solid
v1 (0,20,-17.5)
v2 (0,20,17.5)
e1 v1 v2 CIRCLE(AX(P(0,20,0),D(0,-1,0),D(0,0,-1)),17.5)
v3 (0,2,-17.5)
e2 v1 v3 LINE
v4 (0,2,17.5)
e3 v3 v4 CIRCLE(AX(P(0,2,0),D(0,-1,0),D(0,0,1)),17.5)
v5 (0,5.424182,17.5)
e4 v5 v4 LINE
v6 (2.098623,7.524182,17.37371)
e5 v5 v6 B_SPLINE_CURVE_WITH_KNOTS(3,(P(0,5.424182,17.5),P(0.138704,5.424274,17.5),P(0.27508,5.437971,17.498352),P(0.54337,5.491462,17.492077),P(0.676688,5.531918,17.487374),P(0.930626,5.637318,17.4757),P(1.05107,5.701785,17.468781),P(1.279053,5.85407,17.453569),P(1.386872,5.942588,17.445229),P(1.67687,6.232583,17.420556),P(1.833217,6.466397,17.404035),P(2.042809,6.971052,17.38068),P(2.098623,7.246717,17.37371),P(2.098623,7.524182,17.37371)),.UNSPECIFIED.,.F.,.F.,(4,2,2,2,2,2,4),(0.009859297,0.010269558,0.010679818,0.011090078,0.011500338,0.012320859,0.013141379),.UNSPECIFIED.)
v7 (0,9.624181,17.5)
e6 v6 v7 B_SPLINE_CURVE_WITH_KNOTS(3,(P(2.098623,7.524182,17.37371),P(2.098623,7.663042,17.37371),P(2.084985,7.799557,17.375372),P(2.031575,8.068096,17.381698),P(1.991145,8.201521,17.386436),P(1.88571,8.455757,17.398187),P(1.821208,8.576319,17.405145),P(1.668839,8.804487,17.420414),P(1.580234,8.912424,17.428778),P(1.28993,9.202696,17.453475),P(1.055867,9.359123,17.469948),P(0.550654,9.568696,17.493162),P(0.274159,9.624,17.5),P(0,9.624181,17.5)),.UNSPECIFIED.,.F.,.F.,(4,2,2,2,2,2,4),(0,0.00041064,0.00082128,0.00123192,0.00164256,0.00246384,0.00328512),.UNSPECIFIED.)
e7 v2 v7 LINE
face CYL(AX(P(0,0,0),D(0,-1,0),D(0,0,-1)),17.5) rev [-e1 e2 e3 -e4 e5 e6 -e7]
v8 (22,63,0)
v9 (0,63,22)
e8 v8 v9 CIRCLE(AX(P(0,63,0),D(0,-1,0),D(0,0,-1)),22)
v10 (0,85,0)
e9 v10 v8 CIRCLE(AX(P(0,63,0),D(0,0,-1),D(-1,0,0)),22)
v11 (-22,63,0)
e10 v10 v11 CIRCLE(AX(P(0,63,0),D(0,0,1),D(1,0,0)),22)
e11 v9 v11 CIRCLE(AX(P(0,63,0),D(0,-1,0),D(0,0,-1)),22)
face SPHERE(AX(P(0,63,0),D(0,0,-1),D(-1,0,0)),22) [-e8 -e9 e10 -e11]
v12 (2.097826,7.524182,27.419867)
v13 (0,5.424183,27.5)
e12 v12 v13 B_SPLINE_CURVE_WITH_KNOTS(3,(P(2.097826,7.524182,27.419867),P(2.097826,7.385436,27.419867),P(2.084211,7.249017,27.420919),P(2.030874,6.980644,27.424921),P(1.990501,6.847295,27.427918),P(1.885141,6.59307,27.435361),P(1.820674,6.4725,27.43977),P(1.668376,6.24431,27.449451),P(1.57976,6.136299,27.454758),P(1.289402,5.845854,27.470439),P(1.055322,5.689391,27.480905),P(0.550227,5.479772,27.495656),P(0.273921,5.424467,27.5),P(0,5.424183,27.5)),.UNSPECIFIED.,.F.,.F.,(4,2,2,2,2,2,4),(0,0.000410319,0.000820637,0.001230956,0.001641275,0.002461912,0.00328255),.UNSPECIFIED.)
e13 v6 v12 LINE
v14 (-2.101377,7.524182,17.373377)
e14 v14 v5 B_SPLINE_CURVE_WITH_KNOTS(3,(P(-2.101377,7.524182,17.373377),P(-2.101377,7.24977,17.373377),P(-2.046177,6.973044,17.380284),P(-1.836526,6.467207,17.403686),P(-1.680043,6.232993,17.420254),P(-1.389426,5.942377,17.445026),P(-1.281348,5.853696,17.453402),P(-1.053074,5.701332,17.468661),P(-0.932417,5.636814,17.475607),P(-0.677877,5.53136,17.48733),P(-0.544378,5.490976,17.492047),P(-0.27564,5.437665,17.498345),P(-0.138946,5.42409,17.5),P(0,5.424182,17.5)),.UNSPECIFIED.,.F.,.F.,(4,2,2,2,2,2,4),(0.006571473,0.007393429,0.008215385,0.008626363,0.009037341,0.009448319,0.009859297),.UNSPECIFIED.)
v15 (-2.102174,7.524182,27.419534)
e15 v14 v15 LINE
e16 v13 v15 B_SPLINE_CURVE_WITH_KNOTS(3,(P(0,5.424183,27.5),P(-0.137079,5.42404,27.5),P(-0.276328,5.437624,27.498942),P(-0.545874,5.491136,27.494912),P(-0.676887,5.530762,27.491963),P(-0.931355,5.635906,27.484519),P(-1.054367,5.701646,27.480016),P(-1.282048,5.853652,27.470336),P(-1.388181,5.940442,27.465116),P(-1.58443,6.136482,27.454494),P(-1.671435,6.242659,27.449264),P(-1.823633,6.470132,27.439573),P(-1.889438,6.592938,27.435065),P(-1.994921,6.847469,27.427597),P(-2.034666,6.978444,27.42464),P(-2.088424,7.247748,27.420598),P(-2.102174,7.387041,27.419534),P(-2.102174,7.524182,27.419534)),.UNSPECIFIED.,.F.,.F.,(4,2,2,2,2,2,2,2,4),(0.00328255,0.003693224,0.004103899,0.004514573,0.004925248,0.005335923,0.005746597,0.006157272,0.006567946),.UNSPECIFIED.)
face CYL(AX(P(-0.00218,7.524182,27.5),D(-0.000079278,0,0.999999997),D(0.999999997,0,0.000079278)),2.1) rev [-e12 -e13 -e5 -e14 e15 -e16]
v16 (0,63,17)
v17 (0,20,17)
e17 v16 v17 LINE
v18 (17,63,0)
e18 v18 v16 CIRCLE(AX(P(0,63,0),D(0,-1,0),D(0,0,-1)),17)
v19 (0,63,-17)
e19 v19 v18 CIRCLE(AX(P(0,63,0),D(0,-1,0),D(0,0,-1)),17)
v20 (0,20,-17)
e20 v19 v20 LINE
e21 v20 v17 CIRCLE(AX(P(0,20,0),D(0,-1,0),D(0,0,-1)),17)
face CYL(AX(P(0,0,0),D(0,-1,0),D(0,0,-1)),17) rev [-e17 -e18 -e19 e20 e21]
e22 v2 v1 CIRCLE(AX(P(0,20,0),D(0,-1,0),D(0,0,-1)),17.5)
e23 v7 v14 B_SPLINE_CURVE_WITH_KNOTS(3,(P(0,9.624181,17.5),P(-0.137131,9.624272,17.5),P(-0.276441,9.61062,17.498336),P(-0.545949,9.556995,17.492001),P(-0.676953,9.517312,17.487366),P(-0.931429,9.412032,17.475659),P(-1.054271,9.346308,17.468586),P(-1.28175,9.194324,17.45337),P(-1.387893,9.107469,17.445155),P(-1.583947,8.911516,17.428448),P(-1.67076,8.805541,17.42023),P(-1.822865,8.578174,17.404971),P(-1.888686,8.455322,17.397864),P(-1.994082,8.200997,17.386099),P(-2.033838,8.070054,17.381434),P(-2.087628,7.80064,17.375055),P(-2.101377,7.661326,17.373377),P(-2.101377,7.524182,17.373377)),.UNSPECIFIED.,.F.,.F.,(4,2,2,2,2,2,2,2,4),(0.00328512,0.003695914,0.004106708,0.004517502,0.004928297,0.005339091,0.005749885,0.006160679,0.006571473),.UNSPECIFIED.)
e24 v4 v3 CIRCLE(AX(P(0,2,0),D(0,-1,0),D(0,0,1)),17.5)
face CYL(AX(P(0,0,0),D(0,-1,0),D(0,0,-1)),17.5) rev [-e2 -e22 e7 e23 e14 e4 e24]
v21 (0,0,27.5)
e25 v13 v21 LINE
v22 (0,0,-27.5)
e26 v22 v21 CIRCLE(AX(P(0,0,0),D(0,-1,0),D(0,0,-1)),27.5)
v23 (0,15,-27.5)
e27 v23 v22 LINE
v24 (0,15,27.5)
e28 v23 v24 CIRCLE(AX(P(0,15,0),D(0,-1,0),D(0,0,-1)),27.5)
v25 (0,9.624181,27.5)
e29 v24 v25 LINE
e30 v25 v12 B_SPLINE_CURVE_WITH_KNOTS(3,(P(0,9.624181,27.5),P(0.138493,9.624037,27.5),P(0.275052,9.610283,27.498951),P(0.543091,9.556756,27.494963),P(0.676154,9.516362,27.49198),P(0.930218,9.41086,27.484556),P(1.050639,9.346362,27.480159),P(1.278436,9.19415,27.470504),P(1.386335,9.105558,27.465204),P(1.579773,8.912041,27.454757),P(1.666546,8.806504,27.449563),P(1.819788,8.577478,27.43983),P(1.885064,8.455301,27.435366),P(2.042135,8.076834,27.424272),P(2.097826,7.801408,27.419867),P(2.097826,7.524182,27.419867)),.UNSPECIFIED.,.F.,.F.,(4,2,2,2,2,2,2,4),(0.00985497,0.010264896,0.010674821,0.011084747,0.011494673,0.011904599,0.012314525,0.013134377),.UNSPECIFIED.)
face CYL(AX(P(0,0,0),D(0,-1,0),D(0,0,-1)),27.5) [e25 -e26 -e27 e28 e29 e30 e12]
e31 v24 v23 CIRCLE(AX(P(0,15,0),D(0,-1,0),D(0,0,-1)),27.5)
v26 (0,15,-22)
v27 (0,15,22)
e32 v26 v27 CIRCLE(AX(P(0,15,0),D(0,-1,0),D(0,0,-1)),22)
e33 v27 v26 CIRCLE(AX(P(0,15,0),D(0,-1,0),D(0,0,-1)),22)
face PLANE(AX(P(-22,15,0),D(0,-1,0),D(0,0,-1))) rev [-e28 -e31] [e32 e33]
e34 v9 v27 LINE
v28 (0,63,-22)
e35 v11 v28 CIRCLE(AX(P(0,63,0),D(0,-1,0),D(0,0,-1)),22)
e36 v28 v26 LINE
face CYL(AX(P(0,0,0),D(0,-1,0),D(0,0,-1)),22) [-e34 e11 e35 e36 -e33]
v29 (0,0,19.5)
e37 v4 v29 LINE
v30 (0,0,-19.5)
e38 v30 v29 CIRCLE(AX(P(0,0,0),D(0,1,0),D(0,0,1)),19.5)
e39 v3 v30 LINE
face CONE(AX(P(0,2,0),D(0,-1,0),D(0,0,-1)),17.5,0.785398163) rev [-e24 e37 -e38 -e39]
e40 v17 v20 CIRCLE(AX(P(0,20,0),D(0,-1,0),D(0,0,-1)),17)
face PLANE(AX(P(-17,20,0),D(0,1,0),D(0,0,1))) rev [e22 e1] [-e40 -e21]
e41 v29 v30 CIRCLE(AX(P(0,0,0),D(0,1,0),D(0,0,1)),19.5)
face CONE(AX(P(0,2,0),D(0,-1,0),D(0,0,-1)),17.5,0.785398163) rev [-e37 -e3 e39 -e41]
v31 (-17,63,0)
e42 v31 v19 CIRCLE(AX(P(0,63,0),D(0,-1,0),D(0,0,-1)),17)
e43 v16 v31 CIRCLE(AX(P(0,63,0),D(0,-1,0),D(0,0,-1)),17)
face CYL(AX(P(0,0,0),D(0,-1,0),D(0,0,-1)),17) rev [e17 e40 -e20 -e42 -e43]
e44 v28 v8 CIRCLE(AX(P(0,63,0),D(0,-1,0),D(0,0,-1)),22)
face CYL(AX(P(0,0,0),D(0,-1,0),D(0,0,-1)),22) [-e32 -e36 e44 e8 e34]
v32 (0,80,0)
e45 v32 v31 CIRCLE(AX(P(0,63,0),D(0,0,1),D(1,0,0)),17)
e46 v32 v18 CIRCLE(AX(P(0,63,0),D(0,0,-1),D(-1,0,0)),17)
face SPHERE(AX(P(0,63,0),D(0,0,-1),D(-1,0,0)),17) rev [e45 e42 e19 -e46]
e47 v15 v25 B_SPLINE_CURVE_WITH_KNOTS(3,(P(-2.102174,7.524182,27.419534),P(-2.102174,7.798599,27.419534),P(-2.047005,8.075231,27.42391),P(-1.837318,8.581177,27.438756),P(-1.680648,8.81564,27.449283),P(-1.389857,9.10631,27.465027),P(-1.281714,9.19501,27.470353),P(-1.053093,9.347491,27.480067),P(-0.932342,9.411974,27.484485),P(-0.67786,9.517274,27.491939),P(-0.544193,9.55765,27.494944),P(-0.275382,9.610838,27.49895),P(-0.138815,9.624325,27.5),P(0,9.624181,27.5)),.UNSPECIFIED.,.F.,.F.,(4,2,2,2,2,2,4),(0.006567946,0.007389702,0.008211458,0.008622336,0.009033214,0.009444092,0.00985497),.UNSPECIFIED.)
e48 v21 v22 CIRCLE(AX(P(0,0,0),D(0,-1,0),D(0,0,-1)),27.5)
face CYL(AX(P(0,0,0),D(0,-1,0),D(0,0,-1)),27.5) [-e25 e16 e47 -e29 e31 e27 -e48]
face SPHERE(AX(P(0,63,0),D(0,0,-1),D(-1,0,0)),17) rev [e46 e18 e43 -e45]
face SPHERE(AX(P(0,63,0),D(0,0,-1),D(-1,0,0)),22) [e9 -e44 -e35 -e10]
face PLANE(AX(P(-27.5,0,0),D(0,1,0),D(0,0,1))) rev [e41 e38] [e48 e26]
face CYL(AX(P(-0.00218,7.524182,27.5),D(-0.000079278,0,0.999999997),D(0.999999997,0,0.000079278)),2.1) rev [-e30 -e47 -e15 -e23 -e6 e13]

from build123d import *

# Parameters (mm, degrees)
M5_TAPPED_HOLE1_D     = 4.2
M5_TAPPED_HOLE1_DEPTH = 30
M5_TAPPED_HOLE1_TIP   = 1.2618073
CHAMFER1_SIZE         = 2


with BuildPart() as part:
    # Sketch1 → Revolve2 (revolve)
    with BuildSketch(Plane.XY, mode=Mode.PRIVATE) as revolve2_sk:
        with BuildLine():
            Line((-22, 63), (-22, 15))
            Line((-22, 15), (-27.5, 15))
            Line((-27.5, 15), (-27.5, 0))
            Line((-27.5, 0), (-17.5, 0))
            Line((-17.5, 0), (-17.5, 20))
            Line((-17.5, 20), (-17, 20))
            Line((-17, 20), (-17, 63))
            ThreePointArc((-17, 63), (-12.02081528, 75.02081528), (0, 80))
            Line((0, 80), (0, 85))
            ThreePointArc((0, 85), (-15.556349186, 78.556349186), (-22, 63))
        make_face()
    revolve(revolve2_sk.sketch.rotate(Axis((0, 0, 0), (0, 1, 0)), 270), axis=Axis((0, 0, 0), (0, 1, 0)))

    # M5 Tapped Hole1
    with Locations(Plane(origin=(-0.002180136, 7.524181673, 27.499999914), x_dir=(0.999999996858, 0, 7.9277686e-05), z_dir=(-7.9277686e-05, 0, 0.999999996858))):
        with Locations((0, 0)):
            Hole(M5_TAPPED_HOLE1_D / 2, depth=M5_TAPPED_HOLE1_DEPTH)
            with Locations((0, 0, -(M5_TAPPED_HOLE1_DEPTH + M5_TAPPED_HOLE1_TIP / 2))):  # 118° drill point
                Cone(0, M5_TAPPED_HOLE1_D / 2, M5_TAPPED_HOLE1_TIP, mode=Mode.SUBTRACT)

    # Chamfer1
    chamfer1_edges = [part.edges().sort_by_distance(p)[0] for p in [
        (0, 0, 17.5),
    ]]
    chamfer(chamfer1_edges, length=CHAMFER1_SIZE)


solid = part.part
